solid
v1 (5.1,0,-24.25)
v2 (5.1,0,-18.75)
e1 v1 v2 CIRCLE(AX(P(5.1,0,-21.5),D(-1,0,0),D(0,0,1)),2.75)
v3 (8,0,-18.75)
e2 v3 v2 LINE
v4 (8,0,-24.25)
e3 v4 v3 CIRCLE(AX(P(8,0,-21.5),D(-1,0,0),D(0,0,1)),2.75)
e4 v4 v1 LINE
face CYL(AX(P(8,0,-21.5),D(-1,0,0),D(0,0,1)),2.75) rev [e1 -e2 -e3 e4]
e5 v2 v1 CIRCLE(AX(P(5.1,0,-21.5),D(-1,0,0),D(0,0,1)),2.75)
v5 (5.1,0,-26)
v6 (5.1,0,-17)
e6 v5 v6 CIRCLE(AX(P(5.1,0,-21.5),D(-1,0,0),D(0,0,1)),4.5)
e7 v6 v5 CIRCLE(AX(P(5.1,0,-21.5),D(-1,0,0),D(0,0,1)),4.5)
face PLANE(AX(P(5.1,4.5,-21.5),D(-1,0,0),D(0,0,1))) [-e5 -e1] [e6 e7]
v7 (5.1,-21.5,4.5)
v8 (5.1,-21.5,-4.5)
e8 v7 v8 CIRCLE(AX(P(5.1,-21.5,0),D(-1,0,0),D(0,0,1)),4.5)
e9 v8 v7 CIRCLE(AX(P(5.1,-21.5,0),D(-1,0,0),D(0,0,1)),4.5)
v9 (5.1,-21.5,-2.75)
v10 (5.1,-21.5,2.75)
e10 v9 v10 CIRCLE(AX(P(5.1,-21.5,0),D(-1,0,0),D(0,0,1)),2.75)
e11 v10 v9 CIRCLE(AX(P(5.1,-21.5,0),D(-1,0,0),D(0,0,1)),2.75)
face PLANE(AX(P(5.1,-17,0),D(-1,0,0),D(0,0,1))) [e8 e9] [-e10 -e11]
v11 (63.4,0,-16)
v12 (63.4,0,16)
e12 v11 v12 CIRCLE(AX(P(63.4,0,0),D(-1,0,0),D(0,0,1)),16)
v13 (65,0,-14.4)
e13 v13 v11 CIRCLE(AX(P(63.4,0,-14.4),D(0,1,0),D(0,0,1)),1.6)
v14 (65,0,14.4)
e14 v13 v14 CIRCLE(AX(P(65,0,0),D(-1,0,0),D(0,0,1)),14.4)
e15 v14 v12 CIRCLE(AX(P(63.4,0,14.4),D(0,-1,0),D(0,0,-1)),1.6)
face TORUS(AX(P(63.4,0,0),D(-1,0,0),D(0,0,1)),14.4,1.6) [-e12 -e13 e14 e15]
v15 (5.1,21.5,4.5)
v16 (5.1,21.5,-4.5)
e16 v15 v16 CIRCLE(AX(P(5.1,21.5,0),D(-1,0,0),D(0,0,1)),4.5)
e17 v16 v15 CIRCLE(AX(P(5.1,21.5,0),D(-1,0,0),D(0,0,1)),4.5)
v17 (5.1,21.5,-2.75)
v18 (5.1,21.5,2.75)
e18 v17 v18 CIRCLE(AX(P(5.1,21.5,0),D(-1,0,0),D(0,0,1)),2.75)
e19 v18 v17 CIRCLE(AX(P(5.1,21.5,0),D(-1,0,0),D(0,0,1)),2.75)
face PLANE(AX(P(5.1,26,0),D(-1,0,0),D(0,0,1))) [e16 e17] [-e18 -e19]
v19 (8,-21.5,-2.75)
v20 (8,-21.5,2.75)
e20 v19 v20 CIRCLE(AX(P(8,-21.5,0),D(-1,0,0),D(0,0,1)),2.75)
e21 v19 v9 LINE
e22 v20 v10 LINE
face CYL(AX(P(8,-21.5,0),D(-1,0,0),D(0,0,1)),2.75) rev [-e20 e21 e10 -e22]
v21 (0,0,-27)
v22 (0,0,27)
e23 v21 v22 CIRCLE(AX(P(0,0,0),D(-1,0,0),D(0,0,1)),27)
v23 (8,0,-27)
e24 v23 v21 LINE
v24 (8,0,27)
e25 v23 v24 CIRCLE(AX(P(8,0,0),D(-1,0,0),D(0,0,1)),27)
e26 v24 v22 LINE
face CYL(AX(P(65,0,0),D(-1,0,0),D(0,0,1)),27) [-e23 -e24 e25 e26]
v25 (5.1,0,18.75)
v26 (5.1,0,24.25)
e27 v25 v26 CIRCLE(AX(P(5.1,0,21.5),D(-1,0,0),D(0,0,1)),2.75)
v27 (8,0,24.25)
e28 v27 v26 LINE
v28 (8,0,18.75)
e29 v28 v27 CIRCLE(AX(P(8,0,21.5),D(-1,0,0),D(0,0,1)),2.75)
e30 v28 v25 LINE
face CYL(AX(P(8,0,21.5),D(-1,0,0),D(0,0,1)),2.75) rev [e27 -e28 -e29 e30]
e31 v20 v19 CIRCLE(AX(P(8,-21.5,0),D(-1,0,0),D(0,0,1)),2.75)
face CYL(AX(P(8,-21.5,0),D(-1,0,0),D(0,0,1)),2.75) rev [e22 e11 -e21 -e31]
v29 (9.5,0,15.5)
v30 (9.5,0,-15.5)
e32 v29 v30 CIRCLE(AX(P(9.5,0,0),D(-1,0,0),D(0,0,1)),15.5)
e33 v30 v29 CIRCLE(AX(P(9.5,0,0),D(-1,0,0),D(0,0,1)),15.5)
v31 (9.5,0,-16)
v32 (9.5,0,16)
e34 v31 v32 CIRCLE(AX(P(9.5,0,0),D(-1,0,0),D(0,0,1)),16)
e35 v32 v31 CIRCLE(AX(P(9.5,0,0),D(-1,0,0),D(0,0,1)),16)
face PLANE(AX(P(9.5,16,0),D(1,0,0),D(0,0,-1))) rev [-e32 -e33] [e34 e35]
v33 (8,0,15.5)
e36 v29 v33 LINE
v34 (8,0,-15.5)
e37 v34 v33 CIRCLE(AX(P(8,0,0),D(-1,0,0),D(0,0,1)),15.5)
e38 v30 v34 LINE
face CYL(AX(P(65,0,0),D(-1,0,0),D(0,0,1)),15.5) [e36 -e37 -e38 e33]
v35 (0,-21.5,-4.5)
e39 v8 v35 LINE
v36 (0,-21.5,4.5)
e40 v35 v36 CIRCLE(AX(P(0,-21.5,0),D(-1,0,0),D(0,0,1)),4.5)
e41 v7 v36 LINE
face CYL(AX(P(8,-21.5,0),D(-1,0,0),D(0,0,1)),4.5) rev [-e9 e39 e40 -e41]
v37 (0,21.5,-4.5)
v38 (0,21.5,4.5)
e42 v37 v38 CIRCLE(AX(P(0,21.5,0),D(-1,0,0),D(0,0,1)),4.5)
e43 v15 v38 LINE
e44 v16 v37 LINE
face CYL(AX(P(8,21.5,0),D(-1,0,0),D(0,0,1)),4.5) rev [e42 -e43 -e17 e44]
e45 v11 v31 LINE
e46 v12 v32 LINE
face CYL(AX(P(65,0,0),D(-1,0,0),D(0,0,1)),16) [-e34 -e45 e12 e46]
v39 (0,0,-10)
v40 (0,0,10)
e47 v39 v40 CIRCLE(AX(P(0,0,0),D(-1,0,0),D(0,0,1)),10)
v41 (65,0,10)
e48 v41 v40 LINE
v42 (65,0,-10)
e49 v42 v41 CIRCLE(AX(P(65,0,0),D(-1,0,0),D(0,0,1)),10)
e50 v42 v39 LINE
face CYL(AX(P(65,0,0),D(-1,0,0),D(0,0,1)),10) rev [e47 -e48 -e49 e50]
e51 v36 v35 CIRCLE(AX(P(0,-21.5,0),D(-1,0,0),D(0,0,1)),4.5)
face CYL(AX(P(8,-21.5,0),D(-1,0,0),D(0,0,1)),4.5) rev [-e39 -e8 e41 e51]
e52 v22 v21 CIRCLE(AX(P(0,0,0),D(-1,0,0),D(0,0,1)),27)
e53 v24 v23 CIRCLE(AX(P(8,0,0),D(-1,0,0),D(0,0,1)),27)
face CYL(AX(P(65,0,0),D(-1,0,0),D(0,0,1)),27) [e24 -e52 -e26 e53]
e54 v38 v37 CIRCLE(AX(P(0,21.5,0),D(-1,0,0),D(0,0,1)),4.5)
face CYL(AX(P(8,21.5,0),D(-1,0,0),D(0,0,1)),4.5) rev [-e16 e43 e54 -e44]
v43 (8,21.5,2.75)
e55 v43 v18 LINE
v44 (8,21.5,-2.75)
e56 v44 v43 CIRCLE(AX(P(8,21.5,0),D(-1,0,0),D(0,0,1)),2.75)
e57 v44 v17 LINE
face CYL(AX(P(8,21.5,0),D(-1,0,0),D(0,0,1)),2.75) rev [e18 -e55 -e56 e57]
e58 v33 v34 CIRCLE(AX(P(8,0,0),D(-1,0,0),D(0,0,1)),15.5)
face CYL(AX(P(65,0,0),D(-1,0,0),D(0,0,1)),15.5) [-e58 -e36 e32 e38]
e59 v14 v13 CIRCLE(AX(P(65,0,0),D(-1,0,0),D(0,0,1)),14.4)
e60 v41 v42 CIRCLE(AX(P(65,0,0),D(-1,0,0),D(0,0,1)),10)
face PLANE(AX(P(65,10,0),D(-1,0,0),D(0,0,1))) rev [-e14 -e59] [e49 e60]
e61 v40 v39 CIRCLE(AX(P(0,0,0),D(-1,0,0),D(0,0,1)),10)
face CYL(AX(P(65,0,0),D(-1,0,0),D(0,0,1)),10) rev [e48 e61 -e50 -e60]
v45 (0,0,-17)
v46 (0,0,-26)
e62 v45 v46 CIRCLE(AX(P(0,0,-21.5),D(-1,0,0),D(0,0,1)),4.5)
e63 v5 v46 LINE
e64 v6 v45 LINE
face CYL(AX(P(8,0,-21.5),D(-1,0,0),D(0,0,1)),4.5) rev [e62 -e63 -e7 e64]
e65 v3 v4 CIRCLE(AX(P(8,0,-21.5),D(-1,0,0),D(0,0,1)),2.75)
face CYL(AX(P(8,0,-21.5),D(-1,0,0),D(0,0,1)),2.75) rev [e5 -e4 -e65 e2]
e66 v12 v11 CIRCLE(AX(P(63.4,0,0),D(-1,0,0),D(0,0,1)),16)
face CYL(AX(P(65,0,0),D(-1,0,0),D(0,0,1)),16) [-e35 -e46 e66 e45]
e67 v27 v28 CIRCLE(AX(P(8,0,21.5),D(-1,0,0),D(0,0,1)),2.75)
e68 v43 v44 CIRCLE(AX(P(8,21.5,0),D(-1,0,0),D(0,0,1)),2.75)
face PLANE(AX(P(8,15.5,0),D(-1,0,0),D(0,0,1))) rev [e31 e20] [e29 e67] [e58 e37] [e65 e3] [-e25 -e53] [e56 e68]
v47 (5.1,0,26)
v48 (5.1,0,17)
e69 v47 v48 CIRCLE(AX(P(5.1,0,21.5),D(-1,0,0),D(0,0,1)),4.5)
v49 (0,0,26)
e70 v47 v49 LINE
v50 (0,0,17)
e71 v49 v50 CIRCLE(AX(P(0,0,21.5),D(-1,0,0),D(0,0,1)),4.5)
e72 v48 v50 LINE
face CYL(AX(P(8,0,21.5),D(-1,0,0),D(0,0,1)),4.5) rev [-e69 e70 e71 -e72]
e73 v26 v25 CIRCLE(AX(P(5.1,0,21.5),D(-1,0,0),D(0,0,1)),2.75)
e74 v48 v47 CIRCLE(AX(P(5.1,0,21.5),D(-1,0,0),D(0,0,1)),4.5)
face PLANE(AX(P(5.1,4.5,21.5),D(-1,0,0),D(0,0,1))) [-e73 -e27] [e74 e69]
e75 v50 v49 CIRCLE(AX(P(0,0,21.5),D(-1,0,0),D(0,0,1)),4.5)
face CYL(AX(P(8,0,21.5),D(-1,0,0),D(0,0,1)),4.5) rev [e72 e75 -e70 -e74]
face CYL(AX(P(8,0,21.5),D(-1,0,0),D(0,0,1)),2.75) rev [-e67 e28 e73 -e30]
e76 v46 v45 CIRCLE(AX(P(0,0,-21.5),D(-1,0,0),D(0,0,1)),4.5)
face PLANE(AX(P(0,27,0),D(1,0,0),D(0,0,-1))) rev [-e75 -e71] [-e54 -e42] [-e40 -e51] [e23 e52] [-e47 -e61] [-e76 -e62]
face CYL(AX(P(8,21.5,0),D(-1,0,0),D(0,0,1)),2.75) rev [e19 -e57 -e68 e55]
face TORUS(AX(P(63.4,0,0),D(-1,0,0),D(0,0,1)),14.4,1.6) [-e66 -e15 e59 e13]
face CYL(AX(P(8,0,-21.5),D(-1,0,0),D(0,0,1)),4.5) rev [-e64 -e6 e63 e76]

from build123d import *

# Parameters (mm, degrees)
PATTERN_LINEAR_1_COUNT      = 2
PATTERN_LINEAR_1_PITCH      = 30.405591591
PATTERN_LINEAR_1_COUNT_DIR2 = 2
PATTERN_LINEAR_1_PITCH_DIR2 = 30.405591591


with BuildPart() as part:
    # 草图1 → 旋转1 (revolve)
    with BuildSketch(Plane.XY, mode=Mode.PRIVATE) as revolve_1_sk:
        with BuildLine():
            Line((0, 27), (0, 10))
            Line((0, 10), (65, 10))
            Line((65, 10), (65, 14.4))
            ThreePointArc((65, 14.4), (64.53137085, 15.53137085), (63.4, 16))
            Line((63.4, 16), (9.5, 16))
            Line((9.5, 16), (9.5, 15.5))
            Line((9.5, 15.5), (8, 15.5))
            Line((8, 15.5), (8, 27))
            Line((8, 27), (0, 27))
        make_face()
    revolve(revolve_1_sk.sketch.rotate(Axis((65, 0, 0), (-1, 0, 0)), 270), axis=Axis((65, 0, 0), (-1, 0, 0)))

    # 草图2 → 切除-旋转1 (revolve, cut)
    with BuildSketch(Plane.XY, mode=Mode.PRIVATE) as cut_revolve_1_sk:
        Polygon((0, 21.5), (0, 26), (5.1, 26), (5.1, 24.25), (8, 24.25), (8, 21.5), align=None)
    cut_revolve_1 = revolve(cut_revolve_1_sk.sketch.rotate(Axis((8, 21.5, 0), (-1, 0, 0)), 270), axis=Axis((8, 21.5, 0), (-1, 0, 0)), mode=Mode.SUBTRACT)

    # 阵列(线性)1: Cut-Revolve 1 2 × 2
    with Locations(*[Vector(0, -0.7071067811865475, 0.7071067811865477) * (i * PATTERN_LINEAR_1_PITCH) + Vector(0, -0.7071067811865477, -0.7071067811865474) * (j * PATTERN_LINEAR_1_PITCH_DIR2) for i in range(PATTERN_LINEAR_1_COUNT) for j in range(PATTERN_LINEAR_1_COUNT_DIR2) if (i, j) != (0, 0)]):
        add(cut_revolve_1, mode=Mode.SUBTRACT)


solid = part.part
